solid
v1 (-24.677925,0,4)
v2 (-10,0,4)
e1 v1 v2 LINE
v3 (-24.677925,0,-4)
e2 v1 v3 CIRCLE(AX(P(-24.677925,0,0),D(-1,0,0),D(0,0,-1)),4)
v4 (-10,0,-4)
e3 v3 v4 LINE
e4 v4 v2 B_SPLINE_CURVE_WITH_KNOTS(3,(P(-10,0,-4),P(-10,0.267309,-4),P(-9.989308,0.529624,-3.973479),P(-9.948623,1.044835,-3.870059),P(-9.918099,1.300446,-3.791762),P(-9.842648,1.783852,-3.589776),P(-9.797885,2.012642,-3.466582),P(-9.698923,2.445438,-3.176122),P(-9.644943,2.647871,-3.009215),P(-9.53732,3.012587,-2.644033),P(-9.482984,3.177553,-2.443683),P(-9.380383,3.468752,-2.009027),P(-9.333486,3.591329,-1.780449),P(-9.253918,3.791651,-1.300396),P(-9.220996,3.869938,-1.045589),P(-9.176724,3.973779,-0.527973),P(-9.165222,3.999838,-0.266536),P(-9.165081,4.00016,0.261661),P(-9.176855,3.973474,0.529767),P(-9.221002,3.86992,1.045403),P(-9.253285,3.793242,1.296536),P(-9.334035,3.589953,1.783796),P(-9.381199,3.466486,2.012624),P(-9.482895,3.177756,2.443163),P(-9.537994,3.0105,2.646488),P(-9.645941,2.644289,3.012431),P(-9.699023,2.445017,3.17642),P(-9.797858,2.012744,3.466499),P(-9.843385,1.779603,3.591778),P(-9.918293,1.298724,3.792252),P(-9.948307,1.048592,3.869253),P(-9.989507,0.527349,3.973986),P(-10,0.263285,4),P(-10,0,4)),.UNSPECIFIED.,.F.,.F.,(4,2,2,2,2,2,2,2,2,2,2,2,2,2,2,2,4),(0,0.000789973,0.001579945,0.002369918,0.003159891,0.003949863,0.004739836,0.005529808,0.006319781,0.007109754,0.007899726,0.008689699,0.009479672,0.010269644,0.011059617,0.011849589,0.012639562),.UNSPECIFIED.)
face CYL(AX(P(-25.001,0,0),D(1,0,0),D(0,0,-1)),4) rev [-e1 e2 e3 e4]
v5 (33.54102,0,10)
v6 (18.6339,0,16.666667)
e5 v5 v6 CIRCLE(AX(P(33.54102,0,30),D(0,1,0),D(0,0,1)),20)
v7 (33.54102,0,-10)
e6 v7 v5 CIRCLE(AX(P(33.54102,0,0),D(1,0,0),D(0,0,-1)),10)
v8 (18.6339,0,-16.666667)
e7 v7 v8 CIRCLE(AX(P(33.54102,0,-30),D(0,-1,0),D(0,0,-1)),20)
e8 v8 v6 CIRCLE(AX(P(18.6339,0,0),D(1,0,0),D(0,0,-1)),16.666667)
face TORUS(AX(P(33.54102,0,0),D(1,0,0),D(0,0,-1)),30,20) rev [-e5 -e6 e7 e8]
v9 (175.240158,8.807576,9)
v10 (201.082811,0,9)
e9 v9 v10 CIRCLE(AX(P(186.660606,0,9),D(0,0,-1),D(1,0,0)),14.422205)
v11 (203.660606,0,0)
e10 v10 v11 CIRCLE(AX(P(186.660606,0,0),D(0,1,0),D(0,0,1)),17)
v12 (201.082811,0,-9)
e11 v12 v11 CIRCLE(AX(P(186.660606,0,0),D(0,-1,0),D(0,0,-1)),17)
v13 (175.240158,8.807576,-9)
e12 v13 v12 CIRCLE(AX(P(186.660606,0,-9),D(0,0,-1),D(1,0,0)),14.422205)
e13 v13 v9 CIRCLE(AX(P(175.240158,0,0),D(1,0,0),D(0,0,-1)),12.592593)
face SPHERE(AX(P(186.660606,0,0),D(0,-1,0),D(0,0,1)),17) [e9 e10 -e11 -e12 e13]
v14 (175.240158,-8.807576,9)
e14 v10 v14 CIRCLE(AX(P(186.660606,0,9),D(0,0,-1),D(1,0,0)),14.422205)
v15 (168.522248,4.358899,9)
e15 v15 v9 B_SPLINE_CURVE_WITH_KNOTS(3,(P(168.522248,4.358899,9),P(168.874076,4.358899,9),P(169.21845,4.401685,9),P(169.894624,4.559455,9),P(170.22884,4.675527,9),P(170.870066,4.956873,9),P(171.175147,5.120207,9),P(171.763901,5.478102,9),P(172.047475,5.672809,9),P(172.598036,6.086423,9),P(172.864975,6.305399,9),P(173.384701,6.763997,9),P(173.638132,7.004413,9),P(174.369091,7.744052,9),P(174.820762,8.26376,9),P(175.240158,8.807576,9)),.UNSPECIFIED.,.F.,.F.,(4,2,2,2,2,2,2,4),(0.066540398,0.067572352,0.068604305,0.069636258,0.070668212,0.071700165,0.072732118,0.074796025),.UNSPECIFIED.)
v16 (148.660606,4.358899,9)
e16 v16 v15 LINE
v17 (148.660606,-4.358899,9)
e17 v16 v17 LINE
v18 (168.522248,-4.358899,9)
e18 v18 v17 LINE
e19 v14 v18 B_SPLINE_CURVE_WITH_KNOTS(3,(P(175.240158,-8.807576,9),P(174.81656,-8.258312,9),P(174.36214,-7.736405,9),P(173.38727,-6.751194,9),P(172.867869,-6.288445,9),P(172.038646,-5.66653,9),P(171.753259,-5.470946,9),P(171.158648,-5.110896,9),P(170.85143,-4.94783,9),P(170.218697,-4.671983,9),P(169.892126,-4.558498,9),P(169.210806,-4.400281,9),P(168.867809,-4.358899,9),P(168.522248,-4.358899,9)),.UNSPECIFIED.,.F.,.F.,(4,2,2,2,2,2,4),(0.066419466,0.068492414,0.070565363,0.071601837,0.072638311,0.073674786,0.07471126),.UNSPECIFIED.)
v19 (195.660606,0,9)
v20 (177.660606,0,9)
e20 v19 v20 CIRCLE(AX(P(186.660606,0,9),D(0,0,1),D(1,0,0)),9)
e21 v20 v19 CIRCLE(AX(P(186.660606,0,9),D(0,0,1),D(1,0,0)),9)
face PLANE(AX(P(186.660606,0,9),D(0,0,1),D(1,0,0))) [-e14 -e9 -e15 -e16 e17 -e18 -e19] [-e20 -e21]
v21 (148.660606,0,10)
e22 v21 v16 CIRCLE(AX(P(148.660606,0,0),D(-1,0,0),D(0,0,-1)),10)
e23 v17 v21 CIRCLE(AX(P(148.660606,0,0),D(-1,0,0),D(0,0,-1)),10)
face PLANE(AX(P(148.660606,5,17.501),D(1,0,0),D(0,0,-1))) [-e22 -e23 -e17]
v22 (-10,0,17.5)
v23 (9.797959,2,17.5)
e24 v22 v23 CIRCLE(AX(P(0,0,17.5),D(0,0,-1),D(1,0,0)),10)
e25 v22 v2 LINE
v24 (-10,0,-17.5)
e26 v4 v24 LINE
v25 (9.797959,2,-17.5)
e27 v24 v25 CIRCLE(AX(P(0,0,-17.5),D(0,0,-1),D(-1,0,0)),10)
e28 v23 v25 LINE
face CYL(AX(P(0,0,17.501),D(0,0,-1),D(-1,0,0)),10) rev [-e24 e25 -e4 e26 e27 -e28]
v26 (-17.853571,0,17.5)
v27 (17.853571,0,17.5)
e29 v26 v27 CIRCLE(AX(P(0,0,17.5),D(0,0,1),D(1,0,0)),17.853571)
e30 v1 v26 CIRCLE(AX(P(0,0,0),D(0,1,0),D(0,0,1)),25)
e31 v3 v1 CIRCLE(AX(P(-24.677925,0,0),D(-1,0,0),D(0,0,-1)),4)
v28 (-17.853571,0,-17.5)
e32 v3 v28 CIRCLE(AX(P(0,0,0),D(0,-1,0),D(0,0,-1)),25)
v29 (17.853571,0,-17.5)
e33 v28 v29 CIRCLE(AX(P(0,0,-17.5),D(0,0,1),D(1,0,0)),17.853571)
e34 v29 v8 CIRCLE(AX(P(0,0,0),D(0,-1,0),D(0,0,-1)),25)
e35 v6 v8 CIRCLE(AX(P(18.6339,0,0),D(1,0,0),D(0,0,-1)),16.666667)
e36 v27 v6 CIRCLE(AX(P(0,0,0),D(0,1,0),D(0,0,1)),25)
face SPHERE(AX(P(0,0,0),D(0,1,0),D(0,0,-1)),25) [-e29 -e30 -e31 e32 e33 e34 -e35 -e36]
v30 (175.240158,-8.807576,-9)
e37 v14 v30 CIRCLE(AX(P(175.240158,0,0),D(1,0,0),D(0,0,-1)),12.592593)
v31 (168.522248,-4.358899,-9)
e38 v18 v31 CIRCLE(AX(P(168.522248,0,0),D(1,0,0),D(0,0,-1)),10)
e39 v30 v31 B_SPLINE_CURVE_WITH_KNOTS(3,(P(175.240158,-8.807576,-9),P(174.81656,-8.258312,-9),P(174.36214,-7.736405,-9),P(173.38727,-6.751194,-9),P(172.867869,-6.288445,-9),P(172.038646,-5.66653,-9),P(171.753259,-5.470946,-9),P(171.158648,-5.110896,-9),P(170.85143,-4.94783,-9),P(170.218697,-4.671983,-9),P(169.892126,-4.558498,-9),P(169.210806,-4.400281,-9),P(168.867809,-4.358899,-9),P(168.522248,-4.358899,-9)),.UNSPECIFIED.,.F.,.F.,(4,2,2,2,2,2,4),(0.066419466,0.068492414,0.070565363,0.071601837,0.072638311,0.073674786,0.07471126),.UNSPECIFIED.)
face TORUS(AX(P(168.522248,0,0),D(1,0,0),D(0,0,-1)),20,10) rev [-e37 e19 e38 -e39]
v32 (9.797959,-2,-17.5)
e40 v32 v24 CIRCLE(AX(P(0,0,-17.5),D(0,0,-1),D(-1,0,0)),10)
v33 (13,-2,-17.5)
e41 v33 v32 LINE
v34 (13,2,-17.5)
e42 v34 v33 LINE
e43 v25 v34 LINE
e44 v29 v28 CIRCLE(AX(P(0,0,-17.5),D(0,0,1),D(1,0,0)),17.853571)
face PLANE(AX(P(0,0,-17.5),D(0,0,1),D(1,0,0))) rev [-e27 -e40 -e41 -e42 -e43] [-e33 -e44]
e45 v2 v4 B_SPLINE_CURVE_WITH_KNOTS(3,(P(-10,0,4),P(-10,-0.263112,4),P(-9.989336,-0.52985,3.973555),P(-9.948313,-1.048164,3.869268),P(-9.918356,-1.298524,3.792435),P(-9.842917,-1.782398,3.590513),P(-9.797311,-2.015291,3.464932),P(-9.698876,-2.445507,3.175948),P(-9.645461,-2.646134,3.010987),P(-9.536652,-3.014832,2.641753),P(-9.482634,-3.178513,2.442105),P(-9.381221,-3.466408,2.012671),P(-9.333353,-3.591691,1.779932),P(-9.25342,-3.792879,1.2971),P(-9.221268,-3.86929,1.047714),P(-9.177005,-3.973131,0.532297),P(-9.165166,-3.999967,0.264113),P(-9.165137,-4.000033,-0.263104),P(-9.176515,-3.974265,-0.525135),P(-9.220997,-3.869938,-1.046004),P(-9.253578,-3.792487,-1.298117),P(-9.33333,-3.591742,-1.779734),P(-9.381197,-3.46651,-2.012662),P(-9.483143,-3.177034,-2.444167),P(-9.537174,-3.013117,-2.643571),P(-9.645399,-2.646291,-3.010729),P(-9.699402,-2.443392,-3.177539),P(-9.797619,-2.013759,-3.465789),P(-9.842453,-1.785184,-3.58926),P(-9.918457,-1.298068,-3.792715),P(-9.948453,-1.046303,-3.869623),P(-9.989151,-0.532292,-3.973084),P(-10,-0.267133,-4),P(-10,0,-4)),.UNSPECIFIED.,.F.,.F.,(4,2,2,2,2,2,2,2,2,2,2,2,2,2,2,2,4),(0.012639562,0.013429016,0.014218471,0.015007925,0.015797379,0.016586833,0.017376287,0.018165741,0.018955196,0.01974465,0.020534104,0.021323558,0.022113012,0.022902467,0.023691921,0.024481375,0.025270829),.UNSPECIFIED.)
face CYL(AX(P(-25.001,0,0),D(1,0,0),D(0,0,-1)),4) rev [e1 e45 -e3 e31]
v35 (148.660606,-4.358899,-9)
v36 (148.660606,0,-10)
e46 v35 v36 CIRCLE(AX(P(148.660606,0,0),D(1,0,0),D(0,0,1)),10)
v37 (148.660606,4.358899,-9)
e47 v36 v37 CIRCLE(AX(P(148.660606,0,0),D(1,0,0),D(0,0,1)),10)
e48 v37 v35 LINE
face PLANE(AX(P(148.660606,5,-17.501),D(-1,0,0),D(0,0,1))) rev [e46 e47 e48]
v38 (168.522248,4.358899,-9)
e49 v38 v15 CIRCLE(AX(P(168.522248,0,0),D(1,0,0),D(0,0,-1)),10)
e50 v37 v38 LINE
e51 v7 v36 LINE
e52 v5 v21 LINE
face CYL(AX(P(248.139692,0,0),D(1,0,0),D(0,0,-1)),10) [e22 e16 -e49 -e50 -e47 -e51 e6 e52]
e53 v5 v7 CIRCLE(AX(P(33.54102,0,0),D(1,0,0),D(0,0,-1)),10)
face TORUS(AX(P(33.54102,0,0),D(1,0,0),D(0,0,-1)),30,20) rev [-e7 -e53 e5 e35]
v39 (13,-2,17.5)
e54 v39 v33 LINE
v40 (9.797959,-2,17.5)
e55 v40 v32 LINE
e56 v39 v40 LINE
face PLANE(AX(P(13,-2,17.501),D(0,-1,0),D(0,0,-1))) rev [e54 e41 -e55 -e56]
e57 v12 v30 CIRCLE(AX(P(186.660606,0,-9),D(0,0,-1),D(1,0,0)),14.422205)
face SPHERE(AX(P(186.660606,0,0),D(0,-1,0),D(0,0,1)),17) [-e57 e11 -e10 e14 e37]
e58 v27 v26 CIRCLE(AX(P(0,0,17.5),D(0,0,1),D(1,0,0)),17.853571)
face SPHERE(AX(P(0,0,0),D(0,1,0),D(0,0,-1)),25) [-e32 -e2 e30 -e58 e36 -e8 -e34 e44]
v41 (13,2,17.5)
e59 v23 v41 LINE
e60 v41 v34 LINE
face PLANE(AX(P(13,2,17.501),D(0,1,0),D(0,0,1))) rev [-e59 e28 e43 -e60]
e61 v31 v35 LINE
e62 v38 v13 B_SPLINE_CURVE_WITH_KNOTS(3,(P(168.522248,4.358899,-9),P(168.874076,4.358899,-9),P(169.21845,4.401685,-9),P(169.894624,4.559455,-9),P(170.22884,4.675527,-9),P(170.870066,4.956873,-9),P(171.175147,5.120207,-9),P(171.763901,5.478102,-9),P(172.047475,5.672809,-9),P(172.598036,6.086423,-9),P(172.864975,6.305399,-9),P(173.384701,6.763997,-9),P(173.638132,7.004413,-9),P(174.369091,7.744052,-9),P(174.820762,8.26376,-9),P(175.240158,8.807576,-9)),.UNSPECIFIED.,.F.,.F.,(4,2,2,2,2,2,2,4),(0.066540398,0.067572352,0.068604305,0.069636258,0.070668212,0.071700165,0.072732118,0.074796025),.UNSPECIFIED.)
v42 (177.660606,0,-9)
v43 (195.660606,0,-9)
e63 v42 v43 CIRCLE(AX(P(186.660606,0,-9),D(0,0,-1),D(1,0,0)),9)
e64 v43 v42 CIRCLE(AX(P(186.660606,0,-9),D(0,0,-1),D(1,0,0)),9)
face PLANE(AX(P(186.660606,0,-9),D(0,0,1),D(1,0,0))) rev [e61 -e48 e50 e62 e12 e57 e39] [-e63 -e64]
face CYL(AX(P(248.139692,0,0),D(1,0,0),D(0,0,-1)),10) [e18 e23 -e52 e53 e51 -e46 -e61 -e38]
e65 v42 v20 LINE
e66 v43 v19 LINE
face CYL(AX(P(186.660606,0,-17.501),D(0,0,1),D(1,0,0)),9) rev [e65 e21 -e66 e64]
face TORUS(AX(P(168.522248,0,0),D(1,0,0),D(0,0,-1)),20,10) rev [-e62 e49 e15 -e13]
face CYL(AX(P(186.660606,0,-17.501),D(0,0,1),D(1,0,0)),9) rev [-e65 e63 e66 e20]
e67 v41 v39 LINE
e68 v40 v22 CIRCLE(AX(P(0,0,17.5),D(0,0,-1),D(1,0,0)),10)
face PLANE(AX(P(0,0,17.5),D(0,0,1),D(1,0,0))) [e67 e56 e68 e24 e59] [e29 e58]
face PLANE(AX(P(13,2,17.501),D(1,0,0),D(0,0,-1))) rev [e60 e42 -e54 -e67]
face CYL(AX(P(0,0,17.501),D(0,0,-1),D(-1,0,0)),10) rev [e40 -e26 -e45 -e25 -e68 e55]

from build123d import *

# Parameters (mm, degrees)
BALL_FACE_1_SKETCH_R       = 25
BALL_FACE_CUT_1_DEPTH      = 7.5
BALL_FACE_2_SKETCH_R       = 25
BALL_FACE_CUT_2_DEPTH      = 7.5
KEYED_BORE_20_REACH        = 210.153
SMALL_END_FLAT_CUT_1_REACH = 216.934
SMALL_START                = -9
SMALL_END_FLAT_CUT_2_REACH = 216.934
SMALL_START_2              = 9
SMALL_END_EYE_CUT_REACH    = 208.893
SMALL_END_EYE_SKETCH_R     = 9
HOLE_8_CUT_REACH           = 207.934
HOLE_8_CUT_END_RADIUS      = 25
HOLE_8_SKETCH_R            = 4


with BuildPart() as part:
    # Lever Profile Sketch → Lever Body Revolve (revolve)
    with BuildSketch(Plane(origin=(0, 0, 0), x_dir=(1, 0, 0), z_dir=(0, 1, 0)), mode=Mode.PRIVATE) as lever_body_revolve_sk:
        with BuildLine():
            Line((168.522248412, -10), (33.541019662, -10))
            ThreePointArc((33.541019662, -10), (25.376053853, -11.742581416), (18.633899812, -16.666666667))
            ThreePointArc((18.633899812, -16.666666667), (-8.920552244, -23.354308974), (-25, 0))
            Line((-25, 0), (203.66060556, 0))
            ThreePointArc((203.66060556, 0), (193.547273819, -15.542644572), (175.240158467, -12.592592593))
            ThreePointArc((175.240158467, -12.592592593), (172.122659912, -10.670635765), (168.522248412, -10))
        make_face()
    revolve(lever_body_revolve_sk.sketch.rotate(Axis((248.139692176, 0, 0), (-1, 0, 0)), 180), axis=Axis((248.139692176, 0, 0), (-1, 0, 0)))

    # Ball Face 1 Sketch → Ball Face Cut 1 (cut)
    with BuildSketch(Plane.XY.offset(25)):
        Circle(BALL_FACE_1_SKETCH_R)
    extrude(amount=-BALL_FACE_CUT_1_DEPTH, mode=Mode.SUBTRACT)


with BuildPart() as ball_face_cut_1_kept_piece:
    # of the separate pieces the step leaves, the one the design keeps (ball_face_cut_1_pieces_kept)
    add(part.part.solids().sort_by_distance((175.240158467, 0, -12.592592593))[0])

    # Ball Face 2 Sketch → Ball Face Cut 2 (cut)
    with BuildSketch(Plane.XY.offset(-25)):
        Circle(BALL_FACE_2_SKETCH_R)
    extrude(amount=BALL_FACE_CUT_2_DEPTH, mode=Mode.SUBTRACT)

    # Keyed Bore Sketch → Keyed Bore _20 (cut, up to next)
    with BuildSketch(Plane(origin=(0, 0, -17.5), x_dir=(-1, 0, 0), z_dir=(0, 0, -1)), mode=Mode.PRIVATE) as keyed_bore_20_sk1:
        with BuildLine():
            Line((-13, 2), (-9.797958971, 2))
            ThreePointArc((-9.797958971, 2), (10, 0), (-9.797958971, -2))
            Line((-9.797958971, -2), (-13, -2))
            Line((-13, -2), (-13, 2))
        make_face()
    keyed_bore_20_tool1 = extrude(keyed_bore_20_sk1.sketch, amount=-KEYED_BORE_20_REACH, mode=Mode.PRIVATE) & ball_face_cut_1_kept_piece.part
    add(keyed_bore_20_tool1.solids().sort_by_distance((0.430928, 0, -17.5))[0], mode=Mode.SUBTRACT)

    # Small End Flats Sketch → Small End Flat Cut 1 (cut, up to next)
    with BuildSketch(Plane.XY.offset(SMALL_START), mode=Mode.PRIVATE) as small_end_flat_cut_1_sk1:
        with BuildLine():
            Line((170.41252875, 5), (148.66060556, 5))
            Line((148.66060556, 5), (148.66060556, -5))
            Line((148.66060556, -5), (170.41252875, -5))
            ThreePointArc((170.41252875, -5), (203.66060556, 0), (170.41252875, 5))
        make_face()
    small_end_flat_cut_1_tool1 = extrude(small_end_flat_cut_1_sk1.sketch, amount=-SMALL_END_FLAT_CUT_1_REACH, mode=Mode.PRIVATE) & ball_face_cut_1_kept_piece.part
    add(small_end_flat_cut_1_tool1.solids().sort_by_distance((181.469026, 0, -9))[0], mode=Mode.SUBTRACT)

    # Sketch11_2 → Small End Flat Cut 2 (cut, up to next)
    with BuildSketch(Plane.XY.offset(SMALL_START_2), mode=Mode.PRIVATE) as small_end_flat_cut_2_sk1:
        with BuildLine():
            Line((170.41252875, 5), (148.66060556, 5))
            Line((148.66060556, 5), (148.66060556, -5))
            Line((148.66060556, -5), (170.41252875, -5))
            ThreePointArc((170.41252875, -5), (203.66060556, 0), (170.41252875, 5))
        make_face()
    small_end_flat_cut_2_tool1 = extrude(small_end_flat_cut_2_sk1.sketch, amount=SMALL_END_FLAT_CUT_2_REACH, mode=Mode.PRIVATE) & ball_face_cut_1_kept_piece.part
    add(small_end_flat_cut_2_tool1.solids().sort_by_distance((181.469026, 0, 9))[0], mode=Mode.SUBTRACT)

    # Small End Eye Sketch → Small End Eye Cut (cut, up to next)
    with BuildSketch(Plane.XY.offset(9), mode=Mode.PRIVATE) as small_end_eye_cut_sk1:
        with Locations((186.66060556, 0)):
            Circle(SMALL_END_EYE_SKETCH_R)
    small_end_eye_cut_tool1 = extrude(small_end_eye_cut_sk1.sketch, amount=-SMALL_END_EYE_CUT_REACH, mode=Mode.PRIVATE) & ball_face_cut_1_kept_piece.part
    add(small_end_eye_cut_tool1.solids().sort_by_distance((186.660606, 0, 9))[0], mode=Mode.SUBTRACT)

    # Hole _8 Cut: up to this sphere (the profile starts inside it)
    hole_8_cut_end = Location((0, 0, 0)) * Sphere(HOLE_8_CUT_END_RADIUS, mode=Mode.PRIVATE)
    # Hole _8 Sketch → Hole _8 Cut (cut, up to the surface)
    with BuildSketch(Plane(origin=(0, 0, 0), x_dir=(0, 0, -1), z_dir=(1, 0, 0)), mode=Mode.PRIVATE) as hole_8_cut_sk1:
        Circle(HOLE_8_SKETCH_R)
    hole_8_cut_tool1 = extrude(hole_8_cut_sk1.sketch, amount=-HOLE_8_CUT_REACH, mode=Mode.PRIVATE) & hole_8_cut_end
    add(hole_8_cut_tool1.solids().sort_by_distance((0, 0, 0))[0], mode=Mode.SUBTRACT)


solid = ball_face_cut_1_kept_piece.part
